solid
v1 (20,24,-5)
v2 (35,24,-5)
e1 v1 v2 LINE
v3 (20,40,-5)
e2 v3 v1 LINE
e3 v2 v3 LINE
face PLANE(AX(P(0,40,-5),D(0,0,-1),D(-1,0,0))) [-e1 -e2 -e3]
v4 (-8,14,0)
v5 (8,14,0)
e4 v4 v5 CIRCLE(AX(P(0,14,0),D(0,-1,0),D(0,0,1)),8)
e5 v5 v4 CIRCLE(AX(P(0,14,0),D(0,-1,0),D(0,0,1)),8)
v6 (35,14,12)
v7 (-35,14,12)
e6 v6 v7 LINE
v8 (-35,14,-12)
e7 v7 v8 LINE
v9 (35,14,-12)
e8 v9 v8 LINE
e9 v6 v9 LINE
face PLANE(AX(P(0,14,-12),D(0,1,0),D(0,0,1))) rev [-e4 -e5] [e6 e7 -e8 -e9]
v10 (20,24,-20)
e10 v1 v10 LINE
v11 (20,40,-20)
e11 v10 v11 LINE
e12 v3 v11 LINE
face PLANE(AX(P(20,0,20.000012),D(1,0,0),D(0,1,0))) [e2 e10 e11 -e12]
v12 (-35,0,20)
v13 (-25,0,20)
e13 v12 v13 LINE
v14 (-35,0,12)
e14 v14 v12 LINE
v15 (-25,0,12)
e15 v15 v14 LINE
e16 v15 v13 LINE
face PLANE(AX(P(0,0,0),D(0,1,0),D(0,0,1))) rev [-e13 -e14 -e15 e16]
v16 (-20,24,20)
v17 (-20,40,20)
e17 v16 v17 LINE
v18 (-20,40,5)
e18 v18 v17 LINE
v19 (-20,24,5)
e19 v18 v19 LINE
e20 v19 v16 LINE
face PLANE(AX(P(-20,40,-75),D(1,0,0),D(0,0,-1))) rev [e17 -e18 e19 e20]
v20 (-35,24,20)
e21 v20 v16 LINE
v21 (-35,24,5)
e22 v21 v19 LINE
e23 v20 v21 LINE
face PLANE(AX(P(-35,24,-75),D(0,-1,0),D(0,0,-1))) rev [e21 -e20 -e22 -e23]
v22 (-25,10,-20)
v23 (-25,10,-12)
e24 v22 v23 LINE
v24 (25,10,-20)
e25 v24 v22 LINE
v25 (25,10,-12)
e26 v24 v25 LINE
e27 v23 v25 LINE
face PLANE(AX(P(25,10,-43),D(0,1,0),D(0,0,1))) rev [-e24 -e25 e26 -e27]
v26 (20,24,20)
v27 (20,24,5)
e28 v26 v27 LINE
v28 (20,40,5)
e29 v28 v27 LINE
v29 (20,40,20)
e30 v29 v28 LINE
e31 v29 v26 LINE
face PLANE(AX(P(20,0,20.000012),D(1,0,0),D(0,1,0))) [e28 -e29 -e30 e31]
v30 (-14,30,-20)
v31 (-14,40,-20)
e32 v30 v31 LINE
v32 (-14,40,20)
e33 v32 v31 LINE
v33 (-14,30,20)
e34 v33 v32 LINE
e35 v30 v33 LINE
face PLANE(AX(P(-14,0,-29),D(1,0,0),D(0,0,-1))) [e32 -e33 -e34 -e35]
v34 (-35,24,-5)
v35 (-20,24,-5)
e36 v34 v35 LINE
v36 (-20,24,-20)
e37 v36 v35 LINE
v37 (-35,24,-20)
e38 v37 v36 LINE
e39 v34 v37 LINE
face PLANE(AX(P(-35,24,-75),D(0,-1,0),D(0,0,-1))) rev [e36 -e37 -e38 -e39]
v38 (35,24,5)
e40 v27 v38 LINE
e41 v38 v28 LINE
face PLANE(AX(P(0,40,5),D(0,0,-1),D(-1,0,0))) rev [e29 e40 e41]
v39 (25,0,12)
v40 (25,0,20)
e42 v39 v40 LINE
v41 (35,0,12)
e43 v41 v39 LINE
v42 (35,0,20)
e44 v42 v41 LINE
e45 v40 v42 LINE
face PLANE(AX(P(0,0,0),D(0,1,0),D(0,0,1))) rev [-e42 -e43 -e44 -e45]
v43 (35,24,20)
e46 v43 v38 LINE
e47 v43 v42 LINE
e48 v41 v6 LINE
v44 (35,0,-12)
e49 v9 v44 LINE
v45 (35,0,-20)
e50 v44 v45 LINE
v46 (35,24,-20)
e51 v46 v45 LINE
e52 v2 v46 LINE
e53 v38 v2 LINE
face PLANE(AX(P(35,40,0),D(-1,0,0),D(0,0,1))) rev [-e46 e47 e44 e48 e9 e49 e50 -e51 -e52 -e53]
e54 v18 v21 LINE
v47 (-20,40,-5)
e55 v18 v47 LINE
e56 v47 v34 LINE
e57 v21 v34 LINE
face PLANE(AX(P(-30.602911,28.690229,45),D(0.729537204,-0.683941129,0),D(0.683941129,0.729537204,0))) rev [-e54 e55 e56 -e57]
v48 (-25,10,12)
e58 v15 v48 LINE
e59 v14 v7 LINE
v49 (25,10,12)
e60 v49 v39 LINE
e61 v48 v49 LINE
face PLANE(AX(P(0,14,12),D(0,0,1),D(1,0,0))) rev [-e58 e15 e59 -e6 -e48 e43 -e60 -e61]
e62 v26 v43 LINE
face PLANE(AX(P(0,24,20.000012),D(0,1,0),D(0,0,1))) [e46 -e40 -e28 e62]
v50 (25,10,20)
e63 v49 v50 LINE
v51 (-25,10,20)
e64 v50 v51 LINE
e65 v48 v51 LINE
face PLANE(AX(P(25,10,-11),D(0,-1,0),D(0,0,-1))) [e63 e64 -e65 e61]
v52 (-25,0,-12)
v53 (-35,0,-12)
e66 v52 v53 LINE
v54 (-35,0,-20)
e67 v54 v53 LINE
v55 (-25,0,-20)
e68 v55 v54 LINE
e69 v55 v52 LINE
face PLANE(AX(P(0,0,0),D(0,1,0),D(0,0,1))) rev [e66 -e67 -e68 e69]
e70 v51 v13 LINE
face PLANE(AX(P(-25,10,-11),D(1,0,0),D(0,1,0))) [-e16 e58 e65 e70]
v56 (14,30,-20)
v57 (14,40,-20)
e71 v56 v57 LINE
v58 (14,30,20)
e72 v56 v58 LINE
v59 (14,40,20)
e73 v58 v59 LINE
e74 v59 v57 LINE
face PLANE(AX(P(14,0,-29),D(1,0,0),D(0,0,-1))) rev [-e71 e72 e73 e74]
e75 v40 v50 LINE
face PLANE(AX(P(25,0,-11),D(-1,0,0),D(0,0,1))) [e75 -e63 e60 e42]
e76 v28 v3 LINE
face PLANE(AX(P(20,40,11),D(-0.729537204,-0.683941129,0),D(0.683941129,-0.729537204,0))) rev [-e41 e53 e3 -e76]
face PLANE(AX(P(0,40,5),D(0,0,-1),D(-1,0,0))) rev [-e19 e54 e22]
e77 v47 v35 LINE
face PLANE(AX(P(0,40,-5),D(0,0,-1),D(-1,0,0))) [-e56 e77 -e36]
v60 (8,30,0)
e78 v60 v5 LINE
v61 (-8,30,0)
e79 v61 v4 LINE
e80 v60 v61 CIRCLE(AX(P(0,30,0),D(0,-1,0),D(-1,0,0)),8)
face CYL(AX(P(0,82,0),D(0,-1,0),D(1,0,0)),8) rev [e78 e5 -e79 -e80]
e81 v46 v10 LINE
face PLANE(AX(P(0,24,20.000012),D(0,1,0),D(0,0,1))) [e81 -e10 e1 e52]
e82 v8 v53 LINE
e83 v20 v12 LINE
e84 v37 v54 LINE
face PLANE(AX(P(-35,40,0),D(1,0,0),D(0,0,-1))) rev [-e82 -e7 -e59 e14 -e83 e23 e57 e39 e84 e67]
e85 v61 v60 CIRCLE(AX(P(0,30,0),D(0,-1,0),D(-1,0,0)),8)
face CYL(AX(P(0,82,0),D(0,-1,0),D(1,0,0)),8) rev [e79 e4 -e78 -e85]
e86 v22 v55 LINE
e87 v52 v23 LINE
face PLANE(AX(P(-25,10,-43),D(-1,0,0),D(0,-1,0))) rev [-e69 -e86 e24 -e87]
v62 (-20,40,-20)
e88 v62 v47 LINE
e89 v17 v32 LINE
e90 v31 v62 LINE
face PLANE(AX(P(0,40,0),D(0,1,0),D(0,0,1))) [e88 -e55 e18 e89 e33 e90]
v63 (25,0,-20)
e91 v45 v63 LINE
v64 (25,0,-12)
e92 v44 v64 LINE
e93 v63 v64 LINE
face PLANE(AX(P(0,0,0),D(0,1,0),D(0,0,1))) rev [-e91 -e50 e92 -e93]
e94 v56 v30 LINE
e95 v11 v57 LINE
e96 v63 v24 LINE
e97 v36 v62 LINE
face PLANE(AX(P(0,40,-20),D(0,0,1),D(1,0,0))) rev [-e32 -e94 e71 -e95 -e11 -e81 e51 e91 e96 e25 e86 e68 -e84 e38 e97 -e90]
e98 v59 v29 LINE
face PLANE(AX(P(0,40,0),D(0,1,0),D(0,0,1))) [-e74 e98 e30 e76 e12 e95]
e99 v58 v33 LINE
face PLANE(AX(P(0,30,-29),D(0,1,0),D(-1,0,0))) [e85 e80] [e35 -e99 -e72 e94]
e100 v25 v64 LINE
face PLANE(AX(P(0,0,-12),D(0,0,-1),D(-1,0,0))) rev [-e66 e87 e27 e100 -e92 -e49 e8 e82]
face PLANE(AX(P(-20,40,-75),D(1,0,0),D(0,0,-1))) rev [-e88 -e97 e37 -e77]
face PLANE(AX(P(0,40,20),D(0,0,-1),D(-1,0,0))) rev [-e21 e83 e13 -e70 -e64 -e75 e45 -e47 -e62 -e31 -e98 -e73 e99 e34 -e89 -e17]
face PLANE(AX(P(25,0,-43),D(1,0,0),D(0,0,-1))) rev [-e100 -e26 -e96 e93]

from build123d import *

# Parameters (mm, degrees)
BASE_BLOCK_70X40X40_DEPTH        = 40
BOTTOM_SLOT_SKETCH_W             = 24
BOTTOM_SLOT_SKETCH_H             = 14
BOTTOM_SLOT_DEPTH                = 35
BOTTOM_SLOT_EXTENSION_SKETCH_W   = 24
BOTTOM_SLOT_EXTENSION_SKETCH_H   = 14
BOTTOM_SLOT_EXTENSION_DEPTH      = 35
TOP_CHANNEL_SKETCH_W             = 14
TOP_CHANNEL_SKETCH_H             = 10
TOP_CHANNEL_DEPTH                = 49
SIDE_STEP_CUT_A_DEPTH            = 67.520673478
SIDE_STEP_CUT_A_DEPTH_BACK       = 95
SIDE_STEP_CUT_A_SKETCH_W         = 15
SIDE_STEP_CUT_A_SKETCH_H         = 16
SIDE_STEP_CUT_B_SKETCH_W         = 15
SIDE_STEP_CUT_B_SKETCH_H         = 16
SIDE_STEP_CUT_B_DEPTH            = 95
RIB_A_SKETCH_W                   = 15
RIB_A_SKETCH_H                   = 5
RIB_A_DEPTH                      = 16
RIB_A_TRIM_DEPTH                 = 40
RIB_A_TRIM_DEPTH_BACK            = 52
THROUGH_HOLE_16_DEPTH            = 52
THROUGH_HOLE_16_DEPTH_BACK       = 52
THROUGH_HOLE_16_SKETCH_R         = 8
RIB_B_SKETCH_W                   = 15
RIB_B_SKETCH_H                   = 5
RIB_B_DEPTH                      = 16
RIB_B_TRIM_DEPTH                 = 16
FOOT_RELIEF_CUT_DEPTH            = 23
FOOT_RELIEF_CUT_DEPTH_BACK       = 23
FOOT_RELIEF_SKETCH_W             = 50
FOOT_RELIEF_SKETCH_H             = 10
FOOT_RELIEF_EXTENSION_DEPTH      = 23
FOOT_RELIEF_EXTENSION_DEPTH_BACK = 23
FOOT_RELIEF_EXTENSION_SKETCH_W   = 50
FOOT_RELIEF_EXTENSION_SKETCH_H   = 10


with BuildPart() as part:
    # Base Block Sketch → Base Block 70x40x40 (new body)
    with BuildSketch(Plane(origin=(0, 0, 0), x_dir=(1, 0, 0), z_dir=(0, 1, 0))):
        Polygon((0, -20), (0, 0), (0, 20), (-35, 20), (-35, -20), align=None)
        Polygon((0, 20), (0, 0), (0, -20), (35, -20), (35, 20), align=None)
    extrude(amount=BASE_BLOCK_70X40X40_DEPTH)

    # Bottom Slot Sketch → Bottom Slot (cut)
    with BuildSketch(Plane.ZY.offset(35)):
        with Locations((0, 7)):
            Rectangle(BOTTOM_SLOT_SKETCH_W, BOTTOM_SLOT_SKETCH_H)
    extrude(amount=-BOTTOM_SLOT_DEPTH, mode=Mode.SUBTRACT)

    # Bottom Slot Extension Sketch → Bottom Slot Extension (cut)
    with BuildSketch(Plane.ZY):
        with Locations((0, 7)):
            Rectangle(BOTTOM_SLOT_EXTENSION_SKETCH_W, BOTTOM_SLOT_EXTENSION_SKETCH_H)
    extrude(amount=-BOTTOM_SLOT_EXTENSION_DEPTH, mode=Mode.SUBTRACT)

    # Top Channel Sketch → Top Channel (cut)
    with BuildSketch(Plane.XY.offset(20)):
        with Locations((-7, 35)):
            Rectangle(TOP_CHANNEL_SKETCH_W, TOP_CHANNEL_SKETCH_H)
        with Locations((7, 35)):
            Rectangle(TOP_CHANNEL_SKETCH_W, TOP_CHANNEL_SKETCH_H)
    extrude(amount=-TOP_CHANNEL_DEPTH, mode=Mode.SUBTRACT)

    # Side Step Cut A Sketch → Side Step Cut A (cut, two sides: drawn at the far end of the back side and taken through both)
    with BuildSketch(Plane.XY.offset(20).offset(-SIDE_STEP_CUT_A_DEPTH_BACK)):
        with Locations((27.5, 32)):
            Rectangle(SIDE_STEP_CUT_A_SKETCH_W, SIDE_STEP_CUT_A_SKETCH_H)
    extrude(amount=SIDE_STEP_CUT_A_DEPTH + SIDE_STEP_CUT_A_DEPTH_BACK, mode=Mode.SUBTRACT)

    # Side Step Cut B Sketch → Side Step Cut B (cut)
    with BuildSketch(Plane.XY.offset(20)):
        with Locations((-27.5, 32)):
            Rectangle(SIDE_STEP_CUT_B_SKETCH_W, SIDE_STEP_CUT_B_SKETCH_H)
    extrude(amount=-SIDE_STEP_CUT_B_DEPTH, mode=Mode.SUBTRACT)

    # Rib A Sketch → Rib A (add)
    with BuildSketch(Plane(origin=(0, 24, 0), x_dir=(1, 0, 0), z_dir=(0, 1, 0))):
        with Locations((-27.5, -2.5)):
            Rectangle(RIB_A_SKETCH_W, RIB_A_SKETCH_H)
        with Locations((-27.5, 2.5)):
            Rectangle(RIB_A_SKETCH_W, RIB_A_SKETCH_H)
    extrude(amount=RIB_A_DEPTH)

    # Rib A Trim Sketch → Rib A Trim (cut, two sides: drawn at the far end of the back side and taken through both)
    with BuildSketch(Plane.XY.offset(5).offset(-RIB_A_TRIM_DEPTH_BACK)):
        Polygon((-20, 40), (-35, 24), (-35, 40), align=None)
    extrude(amount=RIB_A_TRIM_DEPTH + RIB_A_TRIM_DEPTH_BACK, mode=Mode.SUBTRACT)

    # Through Hole _16 Sketch → Through Hole _16 (cut, two sides: drawn at the far end of the back side and taken through both)
    with BuildSketch(Plane(origin=(0, 30, 0), x_dir=(1, 0, 0), z_dir=(0, 1, 0)).offset(-THROUGH_HOLE_16_DEPTH_BACK)):
        with Locations(Location((0, 0, 0), (0, 0, 270))):
            Circle(THROUGH_HOLE_16_SKETCH_R)
    extrude(amount=THROUGH_HOLE_16_DEPTH + THROUGH_HOLE_16_DEPTH_BACK, mode=Mode.SUBTRACT)

    # Rib B Sketch → Rib B (add)
    with BuildSketch(Plane(origin=(0, 24, 0), x_dir=(1, 0, 0), z_dir=(0, 1, 0))):
        with Locations((27.5, -2.5)):
            Rectangle(RIB_B_SKETCH_W, RIB_B_SKETCH_H)
        with Locations((27.5, 2.5)):
            Rectangle(RIB_B_SKETCH_W, RIB_B_SKETCH_H)
    extrude(amount=RIB_B_DEPTH)

    # Rib B Trim Sketch → Rib B Trim (cut)
    with BuildSketch(Plane(origin=(0, 0, -5), x_dir=(-1, 0, 0), z_dir=(0, 0, -1))):
        Polygon((-20, 40), (-35, 24), (-35, 40), align=None)
    extrude(amount=-RIB_B_TRIM_DEPTH, mode=Mode.SUBTRACT)

    # Foot Relief Sketch → Foot Relief Cut (cut, two sides: drawn at the far end of the back side and taken through both)
    with BuildSketch(Plane(origin=(0, 0, -20), x_dir=(-1, 0, 0), z_dir=(0, 0, -1)).offset(-FOOT_RELIEF_CUT_DEPTH_BACK)):
        with Locations((0, 5)):
            Rectangle(FOOT_RELIEF_SKETCH_W, FOOT_RELIEF_SKETCH_H)
    extrude(amount=FOOT_RELIEF_CUT_DEPTH + FOOT_RELIEF_CUT_DEPTH_BACK, mode=Mode.SUBTRACT)

    # Foot Relief Extension Sketch → Foot Relief Extension (cut, two sides: drawn at the far end of the back side and taken through both)
    with BuildSketch(Plane(origin=(0, 0, 12), x_dir=(-1, 0, 0), z_dir=(0, 0, -1)).offset(-FOOT_RELIEF_EXTENSION_DEPTH_BACK)):
        with Locations((0, 5)):
            Rectangle(FOOT_RELIEF_EXTENSION_SKETCH_W, FOOT_RELIEF_EXTENSION_SKETCH_H)
    extrude(amount=FOOT_RELIEF_EXTENSION_DEPTH + FOOT_RELIEF_EXTENSION_DEPTH_BACK, mode=Mode.SUBTRACT)


solid = part.part
